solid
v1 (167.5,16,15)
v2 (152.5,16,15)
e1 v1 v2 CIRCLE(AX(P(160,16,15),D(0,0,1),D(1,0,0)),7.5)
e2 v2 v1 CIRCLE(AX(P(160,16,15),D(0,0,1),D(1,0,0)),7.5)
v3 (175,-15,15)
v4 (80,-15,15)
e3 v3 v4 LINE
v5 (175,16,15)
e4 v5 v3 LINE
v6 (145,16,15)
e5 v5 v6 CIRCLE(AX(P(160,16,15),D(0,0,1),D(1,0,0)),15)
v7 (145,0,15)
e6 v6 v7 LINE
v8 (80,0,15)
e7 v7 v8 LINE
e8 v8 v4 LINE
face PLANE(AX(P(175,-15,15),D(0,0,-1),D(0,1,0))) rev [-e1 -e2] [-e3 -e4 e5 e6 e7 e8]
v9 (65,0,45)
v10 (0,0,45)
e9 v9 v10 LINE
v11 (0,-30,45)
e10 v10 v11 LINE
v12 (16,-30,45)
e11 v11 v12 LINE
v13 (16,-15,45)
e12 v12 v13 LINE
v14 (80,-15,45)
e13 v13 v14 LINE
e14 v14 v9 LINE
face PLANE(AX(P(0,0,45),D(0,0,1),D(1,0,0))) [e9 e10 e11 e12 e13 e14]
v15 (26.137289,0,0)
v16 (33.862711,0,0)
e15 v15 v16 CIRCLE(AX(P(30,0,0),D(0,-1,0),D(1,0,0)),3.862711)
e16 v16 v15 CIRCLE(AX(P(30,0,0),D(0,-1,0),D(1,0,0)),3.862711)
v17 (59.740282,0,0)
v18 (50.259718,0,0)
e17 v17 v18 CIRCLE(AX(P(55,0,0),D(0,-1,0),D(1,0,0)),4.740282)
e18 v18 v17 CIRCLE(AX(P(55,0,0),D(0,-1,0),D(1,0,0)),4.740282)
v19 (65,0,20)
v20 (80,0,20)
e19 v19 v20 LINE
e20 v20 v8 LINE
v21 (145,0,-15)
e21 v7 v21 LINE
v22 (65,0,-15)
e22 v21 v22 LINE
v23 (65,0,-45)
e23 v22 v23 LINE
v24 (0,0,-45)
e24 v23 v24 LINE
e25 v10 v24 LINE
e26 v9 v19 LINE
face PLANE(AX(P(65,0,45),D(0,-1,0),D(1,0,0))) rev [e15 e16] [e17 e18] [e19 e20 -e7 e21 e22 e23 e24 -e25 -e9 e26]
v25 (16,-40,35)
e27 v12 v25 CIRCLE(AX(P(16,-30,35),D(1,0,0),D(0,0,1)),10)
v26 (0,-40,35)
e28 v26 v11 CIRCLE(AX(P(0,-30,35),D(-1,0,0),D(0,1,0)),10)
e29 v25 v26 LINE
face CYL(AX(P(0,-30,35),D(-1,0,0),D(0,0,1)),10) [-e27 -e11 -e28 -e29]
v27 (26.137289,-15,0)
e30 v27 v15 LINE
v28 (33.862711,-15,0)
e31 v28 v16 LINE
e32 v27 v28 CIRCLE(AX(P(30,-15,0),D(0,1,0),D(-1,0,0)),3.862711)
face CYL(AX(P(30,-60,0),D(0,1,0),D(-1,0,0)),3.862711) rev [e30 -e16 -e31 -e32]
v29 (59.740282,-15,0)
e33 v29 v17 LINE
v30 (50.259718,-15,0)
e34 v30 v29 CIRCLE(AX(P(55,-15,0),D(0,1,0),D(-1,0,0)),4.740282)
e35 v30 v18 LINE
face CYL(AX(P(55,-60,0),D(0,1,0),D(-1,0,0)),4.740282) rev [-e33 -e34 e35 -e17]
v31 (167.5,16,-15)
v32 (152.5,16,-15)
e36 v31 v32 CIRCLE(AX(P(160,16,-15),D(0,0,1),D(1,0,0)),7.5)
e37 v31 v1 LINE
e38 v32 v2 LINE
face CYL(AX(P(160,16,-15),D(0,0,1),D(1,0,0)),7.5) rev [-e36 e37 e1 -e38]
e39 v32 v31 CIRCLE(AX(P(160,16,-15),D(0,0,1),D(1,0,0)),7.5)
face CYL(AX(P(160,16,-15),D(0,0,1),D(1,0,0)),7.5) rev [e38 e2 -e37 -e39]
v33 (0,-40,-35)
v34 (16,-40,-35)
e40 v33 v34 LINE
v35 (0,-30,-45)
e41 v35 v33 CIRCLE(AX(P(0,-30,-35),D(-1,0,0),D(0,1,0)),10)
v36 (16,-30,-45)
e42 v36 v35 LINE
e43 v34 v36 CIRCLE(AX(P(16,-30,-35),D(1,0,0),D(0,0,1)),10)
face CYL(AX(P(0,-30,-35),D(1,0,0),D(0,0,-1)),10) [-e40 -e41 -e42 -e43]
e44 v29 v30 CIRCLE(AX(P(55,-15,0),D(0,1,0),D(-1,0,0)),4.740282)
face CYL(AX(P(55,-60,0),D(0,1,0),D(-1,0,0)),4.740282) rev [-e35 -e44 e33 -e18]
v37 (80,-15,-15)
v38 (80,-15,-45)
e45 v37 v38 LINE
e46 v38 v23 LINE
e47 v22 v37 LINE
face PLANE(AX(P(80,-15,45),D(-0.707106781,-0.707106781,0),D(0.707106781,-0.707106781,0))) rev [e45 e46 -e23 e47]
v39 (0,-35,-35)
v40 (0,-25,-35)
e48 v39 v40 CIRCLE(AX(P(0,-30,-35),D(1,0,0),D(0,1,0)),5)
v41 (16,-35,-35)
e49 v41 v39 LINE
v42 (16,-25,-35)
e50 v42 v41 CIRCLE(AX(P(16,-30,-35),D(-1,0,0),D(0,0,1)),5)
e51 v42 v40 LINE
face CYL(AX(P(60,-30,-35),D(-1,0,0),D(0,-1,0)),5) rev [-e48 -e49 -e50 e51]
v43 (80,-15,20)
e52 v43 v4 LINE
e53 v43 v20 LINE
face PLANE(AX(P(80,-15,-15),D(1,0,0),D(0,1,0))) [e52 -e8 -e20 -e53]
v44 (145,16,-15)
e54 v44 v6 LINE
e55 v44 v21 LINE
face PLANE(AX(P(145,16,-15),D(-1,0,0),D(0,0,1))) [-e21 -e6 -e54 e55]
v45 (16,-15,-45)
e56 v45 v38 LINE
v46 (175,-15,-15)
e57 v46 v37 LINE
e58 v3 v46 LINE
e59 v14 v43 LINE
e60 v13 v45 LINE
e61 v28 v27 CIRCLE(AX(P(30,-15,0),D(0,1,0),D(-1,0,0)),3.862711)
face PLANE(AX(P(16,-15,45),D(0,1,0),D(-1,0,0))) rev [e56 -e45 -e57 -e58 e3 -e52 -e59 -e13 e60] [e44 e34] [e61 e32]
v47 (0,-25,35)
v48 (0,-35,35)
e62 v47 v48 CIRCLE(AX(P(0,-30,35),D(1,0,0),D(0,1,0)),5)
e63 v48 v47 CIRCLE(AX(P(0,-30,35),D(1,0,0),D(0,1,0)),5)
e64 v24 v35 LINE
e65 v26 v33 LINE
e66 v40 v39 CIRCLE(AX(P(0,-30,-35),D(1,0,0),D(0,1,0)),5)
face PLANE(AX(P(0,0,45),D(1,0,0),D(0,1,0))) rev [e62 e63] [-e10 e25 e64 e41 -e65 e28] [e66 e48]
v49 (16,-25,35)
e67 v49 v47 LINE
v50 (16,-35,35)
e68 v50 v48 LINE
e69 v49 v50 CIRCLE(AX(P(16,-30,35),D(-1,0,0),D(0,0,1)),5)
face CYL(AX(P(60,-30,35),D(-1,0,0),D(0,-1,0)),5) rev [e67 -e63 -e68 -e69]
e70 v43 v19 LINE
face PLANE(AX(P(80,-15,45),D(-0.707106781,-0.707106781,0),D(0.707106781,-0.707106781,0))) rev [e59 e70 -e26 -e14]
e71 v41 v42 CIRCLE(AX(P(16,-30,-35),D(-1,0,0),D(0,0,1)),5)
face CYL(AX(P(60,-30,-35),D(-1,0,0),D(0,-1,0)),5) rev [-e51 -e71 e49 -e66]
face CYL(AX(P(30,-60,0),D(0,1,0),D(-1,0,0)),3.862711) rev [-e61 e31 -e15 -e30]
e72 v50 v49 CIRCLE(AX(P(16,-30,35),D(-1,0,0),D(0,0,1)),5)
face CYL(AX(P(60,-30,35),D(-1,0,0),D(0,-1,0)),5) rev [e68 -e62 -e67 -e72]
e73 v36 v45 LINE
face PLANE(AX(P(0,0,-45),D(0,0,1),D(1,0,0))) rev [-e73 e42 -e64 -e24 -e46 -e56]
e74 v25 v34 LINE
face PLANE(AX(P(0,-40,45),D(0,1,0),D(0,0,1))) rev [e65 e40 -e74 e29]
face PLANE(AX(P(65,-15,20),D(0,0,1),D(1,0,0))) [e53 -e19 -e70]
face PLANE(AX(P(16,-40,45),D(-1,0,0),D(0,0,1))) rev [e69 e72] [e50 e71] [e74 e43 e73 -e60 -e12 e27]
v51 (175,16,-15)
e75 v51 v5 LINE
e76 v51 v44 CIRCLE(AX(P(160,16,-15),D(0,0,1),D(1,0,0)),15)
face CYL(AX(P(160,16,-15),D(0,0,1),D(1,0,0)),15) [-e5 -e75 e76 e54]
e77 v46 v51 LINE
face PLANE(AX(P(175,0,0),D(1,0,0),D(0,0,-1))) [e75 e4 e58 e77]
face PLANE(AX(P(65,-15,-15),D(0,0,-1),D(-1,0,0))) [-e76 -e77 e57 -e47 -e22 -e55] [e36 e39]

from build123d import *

# Parameters (mm, degrees)
BASE_BLOCK_DEPTH        = 45
STEP_BOSS_PROFILE_W     = 15
STEP_BOSS_PROFILE_H     = 35
STEP_BOSS_DEPTH         = 15
ARM_PROFILE_W           = 30
ARM_PROFILE_H           = 15
EXTENSION_ARM_DEPTH     = 95
HINGE_LUG_PROFILE_R     = 7.5
HINGE_LUG_DEPTH         = 30
EDGE_FILLET_R10_R       = 10
PIN_HOLES_PROFILE_R     = 5
PIN_HOLES_THROUGH_DEPTH = 60
TOP_HOLES_PROFILE_R     = 3.862710878
TOP_HOLES_PROFILE_R_2   = 4.740282405
TOP_HOLES_THROUGH_DEPTH = 60


with BuildPart() as part:
    # Base Block Profile → Base Block (new, symmetric)
    with BuildSketch(Plane.XY):
        Polygon((0, 0), (0, -40), (16, -40), (16, -15), (80, -15), (65, 0), align=None)
    extrude(amount=BASE_BLOCK_DEPTH, both=True)

    # Step Boss Profile → Step Boss (add)
    with BuildSketch(Plane(origin=(0, 0, 0), x_dir=(1, 0, 0), z_dir=(0, 1, 0))):
        with Locations((72.5, -2.5)):
            Rectangle(STEP_BOSS_PROFILE_W, STEP_BOSS_PROFILE_H)
    extrude(amount=-STEP_BOSS_DEPTH)

    # Arm Profile → Extension Arm (add)
    with BuildSketch(Plane(origin=(80, 0, 0), x_dir=(0, 0, -1), z_dir=(1, 0, 0))):
        with Locations((0, -7.5)):
            Rectangle(ARM_PROFILE_W, ARM_PROFILE_H)
    extrude(amount=EXTENSION_ARM_DEPTH)

    # Hinge Lug Profile → Hinge Lug (add)
    with BuildSketch(Plane.XY.offset(15)):
        with BuildLine():
            Line((145, 16), (145, -10.792045984))
            Line((145, -10.792045984), (175, -10.792045984))
            Line((175, -10.792045984), (175, 16))
            ThreePointArc((175, 16), (160, 31), (145, 16))
        make_face()
        with Locations((160, 16)):
            Circle(HINGE_LUG_PROFILE_R, mode=Mode.SUBTRACT)
    extrude(amount=-HINGE_LUG_DEPTH)

    # Edge Fillet R10
    edge_fillet_r10_edges = [part.edges().sort_by_distance(p)[0] for p in [
        (8, -40, 45),
        (8, -40, -45),
    ]]
    fillet(edge_fillet_r10_edges, radius=EDGE_FILLET_R10_R)

    # Pin Holes Profile → Pin Holes Through (cut, symmetric)
    with BuildSketch(Plane.ZY):
        with Locations(Location((-35, -30, 0), (0, 0, 270))):
            Circle(PIN_HOLES_PROFILE_R)
        with Locations(Location((35, -30, 0), (0, 0, 270))):
            Circle(PIN_HOLES_PROFILE_R)
    extrude(amount=PIN_HOLES_THROUGH_DEPTH, both=True, mode=Mode.SUBTRACT)

    # Top Holes Profile → Top Holes Through (cut, symmetric)
    with BuildSketch(Plane(origin=(0, 0, 0), x_dir=(1, 0, 0), z_dir=(0, 1, 0))):
        with Locations(Location((30, 0, 0), (0, 0, 180))):
            Circle(TOP_HOLES_PROFILE_R)
        with Locations(Location((55, 0, 0), (0, 0, 180))):
            Circle(TOP_HOLES_PROFILE_R_2)
    extrude(amount=TOP_HOLES_THROUGH_DEPTH, both=True, mode=Mode.SUBTRACT)


solid = part.part
